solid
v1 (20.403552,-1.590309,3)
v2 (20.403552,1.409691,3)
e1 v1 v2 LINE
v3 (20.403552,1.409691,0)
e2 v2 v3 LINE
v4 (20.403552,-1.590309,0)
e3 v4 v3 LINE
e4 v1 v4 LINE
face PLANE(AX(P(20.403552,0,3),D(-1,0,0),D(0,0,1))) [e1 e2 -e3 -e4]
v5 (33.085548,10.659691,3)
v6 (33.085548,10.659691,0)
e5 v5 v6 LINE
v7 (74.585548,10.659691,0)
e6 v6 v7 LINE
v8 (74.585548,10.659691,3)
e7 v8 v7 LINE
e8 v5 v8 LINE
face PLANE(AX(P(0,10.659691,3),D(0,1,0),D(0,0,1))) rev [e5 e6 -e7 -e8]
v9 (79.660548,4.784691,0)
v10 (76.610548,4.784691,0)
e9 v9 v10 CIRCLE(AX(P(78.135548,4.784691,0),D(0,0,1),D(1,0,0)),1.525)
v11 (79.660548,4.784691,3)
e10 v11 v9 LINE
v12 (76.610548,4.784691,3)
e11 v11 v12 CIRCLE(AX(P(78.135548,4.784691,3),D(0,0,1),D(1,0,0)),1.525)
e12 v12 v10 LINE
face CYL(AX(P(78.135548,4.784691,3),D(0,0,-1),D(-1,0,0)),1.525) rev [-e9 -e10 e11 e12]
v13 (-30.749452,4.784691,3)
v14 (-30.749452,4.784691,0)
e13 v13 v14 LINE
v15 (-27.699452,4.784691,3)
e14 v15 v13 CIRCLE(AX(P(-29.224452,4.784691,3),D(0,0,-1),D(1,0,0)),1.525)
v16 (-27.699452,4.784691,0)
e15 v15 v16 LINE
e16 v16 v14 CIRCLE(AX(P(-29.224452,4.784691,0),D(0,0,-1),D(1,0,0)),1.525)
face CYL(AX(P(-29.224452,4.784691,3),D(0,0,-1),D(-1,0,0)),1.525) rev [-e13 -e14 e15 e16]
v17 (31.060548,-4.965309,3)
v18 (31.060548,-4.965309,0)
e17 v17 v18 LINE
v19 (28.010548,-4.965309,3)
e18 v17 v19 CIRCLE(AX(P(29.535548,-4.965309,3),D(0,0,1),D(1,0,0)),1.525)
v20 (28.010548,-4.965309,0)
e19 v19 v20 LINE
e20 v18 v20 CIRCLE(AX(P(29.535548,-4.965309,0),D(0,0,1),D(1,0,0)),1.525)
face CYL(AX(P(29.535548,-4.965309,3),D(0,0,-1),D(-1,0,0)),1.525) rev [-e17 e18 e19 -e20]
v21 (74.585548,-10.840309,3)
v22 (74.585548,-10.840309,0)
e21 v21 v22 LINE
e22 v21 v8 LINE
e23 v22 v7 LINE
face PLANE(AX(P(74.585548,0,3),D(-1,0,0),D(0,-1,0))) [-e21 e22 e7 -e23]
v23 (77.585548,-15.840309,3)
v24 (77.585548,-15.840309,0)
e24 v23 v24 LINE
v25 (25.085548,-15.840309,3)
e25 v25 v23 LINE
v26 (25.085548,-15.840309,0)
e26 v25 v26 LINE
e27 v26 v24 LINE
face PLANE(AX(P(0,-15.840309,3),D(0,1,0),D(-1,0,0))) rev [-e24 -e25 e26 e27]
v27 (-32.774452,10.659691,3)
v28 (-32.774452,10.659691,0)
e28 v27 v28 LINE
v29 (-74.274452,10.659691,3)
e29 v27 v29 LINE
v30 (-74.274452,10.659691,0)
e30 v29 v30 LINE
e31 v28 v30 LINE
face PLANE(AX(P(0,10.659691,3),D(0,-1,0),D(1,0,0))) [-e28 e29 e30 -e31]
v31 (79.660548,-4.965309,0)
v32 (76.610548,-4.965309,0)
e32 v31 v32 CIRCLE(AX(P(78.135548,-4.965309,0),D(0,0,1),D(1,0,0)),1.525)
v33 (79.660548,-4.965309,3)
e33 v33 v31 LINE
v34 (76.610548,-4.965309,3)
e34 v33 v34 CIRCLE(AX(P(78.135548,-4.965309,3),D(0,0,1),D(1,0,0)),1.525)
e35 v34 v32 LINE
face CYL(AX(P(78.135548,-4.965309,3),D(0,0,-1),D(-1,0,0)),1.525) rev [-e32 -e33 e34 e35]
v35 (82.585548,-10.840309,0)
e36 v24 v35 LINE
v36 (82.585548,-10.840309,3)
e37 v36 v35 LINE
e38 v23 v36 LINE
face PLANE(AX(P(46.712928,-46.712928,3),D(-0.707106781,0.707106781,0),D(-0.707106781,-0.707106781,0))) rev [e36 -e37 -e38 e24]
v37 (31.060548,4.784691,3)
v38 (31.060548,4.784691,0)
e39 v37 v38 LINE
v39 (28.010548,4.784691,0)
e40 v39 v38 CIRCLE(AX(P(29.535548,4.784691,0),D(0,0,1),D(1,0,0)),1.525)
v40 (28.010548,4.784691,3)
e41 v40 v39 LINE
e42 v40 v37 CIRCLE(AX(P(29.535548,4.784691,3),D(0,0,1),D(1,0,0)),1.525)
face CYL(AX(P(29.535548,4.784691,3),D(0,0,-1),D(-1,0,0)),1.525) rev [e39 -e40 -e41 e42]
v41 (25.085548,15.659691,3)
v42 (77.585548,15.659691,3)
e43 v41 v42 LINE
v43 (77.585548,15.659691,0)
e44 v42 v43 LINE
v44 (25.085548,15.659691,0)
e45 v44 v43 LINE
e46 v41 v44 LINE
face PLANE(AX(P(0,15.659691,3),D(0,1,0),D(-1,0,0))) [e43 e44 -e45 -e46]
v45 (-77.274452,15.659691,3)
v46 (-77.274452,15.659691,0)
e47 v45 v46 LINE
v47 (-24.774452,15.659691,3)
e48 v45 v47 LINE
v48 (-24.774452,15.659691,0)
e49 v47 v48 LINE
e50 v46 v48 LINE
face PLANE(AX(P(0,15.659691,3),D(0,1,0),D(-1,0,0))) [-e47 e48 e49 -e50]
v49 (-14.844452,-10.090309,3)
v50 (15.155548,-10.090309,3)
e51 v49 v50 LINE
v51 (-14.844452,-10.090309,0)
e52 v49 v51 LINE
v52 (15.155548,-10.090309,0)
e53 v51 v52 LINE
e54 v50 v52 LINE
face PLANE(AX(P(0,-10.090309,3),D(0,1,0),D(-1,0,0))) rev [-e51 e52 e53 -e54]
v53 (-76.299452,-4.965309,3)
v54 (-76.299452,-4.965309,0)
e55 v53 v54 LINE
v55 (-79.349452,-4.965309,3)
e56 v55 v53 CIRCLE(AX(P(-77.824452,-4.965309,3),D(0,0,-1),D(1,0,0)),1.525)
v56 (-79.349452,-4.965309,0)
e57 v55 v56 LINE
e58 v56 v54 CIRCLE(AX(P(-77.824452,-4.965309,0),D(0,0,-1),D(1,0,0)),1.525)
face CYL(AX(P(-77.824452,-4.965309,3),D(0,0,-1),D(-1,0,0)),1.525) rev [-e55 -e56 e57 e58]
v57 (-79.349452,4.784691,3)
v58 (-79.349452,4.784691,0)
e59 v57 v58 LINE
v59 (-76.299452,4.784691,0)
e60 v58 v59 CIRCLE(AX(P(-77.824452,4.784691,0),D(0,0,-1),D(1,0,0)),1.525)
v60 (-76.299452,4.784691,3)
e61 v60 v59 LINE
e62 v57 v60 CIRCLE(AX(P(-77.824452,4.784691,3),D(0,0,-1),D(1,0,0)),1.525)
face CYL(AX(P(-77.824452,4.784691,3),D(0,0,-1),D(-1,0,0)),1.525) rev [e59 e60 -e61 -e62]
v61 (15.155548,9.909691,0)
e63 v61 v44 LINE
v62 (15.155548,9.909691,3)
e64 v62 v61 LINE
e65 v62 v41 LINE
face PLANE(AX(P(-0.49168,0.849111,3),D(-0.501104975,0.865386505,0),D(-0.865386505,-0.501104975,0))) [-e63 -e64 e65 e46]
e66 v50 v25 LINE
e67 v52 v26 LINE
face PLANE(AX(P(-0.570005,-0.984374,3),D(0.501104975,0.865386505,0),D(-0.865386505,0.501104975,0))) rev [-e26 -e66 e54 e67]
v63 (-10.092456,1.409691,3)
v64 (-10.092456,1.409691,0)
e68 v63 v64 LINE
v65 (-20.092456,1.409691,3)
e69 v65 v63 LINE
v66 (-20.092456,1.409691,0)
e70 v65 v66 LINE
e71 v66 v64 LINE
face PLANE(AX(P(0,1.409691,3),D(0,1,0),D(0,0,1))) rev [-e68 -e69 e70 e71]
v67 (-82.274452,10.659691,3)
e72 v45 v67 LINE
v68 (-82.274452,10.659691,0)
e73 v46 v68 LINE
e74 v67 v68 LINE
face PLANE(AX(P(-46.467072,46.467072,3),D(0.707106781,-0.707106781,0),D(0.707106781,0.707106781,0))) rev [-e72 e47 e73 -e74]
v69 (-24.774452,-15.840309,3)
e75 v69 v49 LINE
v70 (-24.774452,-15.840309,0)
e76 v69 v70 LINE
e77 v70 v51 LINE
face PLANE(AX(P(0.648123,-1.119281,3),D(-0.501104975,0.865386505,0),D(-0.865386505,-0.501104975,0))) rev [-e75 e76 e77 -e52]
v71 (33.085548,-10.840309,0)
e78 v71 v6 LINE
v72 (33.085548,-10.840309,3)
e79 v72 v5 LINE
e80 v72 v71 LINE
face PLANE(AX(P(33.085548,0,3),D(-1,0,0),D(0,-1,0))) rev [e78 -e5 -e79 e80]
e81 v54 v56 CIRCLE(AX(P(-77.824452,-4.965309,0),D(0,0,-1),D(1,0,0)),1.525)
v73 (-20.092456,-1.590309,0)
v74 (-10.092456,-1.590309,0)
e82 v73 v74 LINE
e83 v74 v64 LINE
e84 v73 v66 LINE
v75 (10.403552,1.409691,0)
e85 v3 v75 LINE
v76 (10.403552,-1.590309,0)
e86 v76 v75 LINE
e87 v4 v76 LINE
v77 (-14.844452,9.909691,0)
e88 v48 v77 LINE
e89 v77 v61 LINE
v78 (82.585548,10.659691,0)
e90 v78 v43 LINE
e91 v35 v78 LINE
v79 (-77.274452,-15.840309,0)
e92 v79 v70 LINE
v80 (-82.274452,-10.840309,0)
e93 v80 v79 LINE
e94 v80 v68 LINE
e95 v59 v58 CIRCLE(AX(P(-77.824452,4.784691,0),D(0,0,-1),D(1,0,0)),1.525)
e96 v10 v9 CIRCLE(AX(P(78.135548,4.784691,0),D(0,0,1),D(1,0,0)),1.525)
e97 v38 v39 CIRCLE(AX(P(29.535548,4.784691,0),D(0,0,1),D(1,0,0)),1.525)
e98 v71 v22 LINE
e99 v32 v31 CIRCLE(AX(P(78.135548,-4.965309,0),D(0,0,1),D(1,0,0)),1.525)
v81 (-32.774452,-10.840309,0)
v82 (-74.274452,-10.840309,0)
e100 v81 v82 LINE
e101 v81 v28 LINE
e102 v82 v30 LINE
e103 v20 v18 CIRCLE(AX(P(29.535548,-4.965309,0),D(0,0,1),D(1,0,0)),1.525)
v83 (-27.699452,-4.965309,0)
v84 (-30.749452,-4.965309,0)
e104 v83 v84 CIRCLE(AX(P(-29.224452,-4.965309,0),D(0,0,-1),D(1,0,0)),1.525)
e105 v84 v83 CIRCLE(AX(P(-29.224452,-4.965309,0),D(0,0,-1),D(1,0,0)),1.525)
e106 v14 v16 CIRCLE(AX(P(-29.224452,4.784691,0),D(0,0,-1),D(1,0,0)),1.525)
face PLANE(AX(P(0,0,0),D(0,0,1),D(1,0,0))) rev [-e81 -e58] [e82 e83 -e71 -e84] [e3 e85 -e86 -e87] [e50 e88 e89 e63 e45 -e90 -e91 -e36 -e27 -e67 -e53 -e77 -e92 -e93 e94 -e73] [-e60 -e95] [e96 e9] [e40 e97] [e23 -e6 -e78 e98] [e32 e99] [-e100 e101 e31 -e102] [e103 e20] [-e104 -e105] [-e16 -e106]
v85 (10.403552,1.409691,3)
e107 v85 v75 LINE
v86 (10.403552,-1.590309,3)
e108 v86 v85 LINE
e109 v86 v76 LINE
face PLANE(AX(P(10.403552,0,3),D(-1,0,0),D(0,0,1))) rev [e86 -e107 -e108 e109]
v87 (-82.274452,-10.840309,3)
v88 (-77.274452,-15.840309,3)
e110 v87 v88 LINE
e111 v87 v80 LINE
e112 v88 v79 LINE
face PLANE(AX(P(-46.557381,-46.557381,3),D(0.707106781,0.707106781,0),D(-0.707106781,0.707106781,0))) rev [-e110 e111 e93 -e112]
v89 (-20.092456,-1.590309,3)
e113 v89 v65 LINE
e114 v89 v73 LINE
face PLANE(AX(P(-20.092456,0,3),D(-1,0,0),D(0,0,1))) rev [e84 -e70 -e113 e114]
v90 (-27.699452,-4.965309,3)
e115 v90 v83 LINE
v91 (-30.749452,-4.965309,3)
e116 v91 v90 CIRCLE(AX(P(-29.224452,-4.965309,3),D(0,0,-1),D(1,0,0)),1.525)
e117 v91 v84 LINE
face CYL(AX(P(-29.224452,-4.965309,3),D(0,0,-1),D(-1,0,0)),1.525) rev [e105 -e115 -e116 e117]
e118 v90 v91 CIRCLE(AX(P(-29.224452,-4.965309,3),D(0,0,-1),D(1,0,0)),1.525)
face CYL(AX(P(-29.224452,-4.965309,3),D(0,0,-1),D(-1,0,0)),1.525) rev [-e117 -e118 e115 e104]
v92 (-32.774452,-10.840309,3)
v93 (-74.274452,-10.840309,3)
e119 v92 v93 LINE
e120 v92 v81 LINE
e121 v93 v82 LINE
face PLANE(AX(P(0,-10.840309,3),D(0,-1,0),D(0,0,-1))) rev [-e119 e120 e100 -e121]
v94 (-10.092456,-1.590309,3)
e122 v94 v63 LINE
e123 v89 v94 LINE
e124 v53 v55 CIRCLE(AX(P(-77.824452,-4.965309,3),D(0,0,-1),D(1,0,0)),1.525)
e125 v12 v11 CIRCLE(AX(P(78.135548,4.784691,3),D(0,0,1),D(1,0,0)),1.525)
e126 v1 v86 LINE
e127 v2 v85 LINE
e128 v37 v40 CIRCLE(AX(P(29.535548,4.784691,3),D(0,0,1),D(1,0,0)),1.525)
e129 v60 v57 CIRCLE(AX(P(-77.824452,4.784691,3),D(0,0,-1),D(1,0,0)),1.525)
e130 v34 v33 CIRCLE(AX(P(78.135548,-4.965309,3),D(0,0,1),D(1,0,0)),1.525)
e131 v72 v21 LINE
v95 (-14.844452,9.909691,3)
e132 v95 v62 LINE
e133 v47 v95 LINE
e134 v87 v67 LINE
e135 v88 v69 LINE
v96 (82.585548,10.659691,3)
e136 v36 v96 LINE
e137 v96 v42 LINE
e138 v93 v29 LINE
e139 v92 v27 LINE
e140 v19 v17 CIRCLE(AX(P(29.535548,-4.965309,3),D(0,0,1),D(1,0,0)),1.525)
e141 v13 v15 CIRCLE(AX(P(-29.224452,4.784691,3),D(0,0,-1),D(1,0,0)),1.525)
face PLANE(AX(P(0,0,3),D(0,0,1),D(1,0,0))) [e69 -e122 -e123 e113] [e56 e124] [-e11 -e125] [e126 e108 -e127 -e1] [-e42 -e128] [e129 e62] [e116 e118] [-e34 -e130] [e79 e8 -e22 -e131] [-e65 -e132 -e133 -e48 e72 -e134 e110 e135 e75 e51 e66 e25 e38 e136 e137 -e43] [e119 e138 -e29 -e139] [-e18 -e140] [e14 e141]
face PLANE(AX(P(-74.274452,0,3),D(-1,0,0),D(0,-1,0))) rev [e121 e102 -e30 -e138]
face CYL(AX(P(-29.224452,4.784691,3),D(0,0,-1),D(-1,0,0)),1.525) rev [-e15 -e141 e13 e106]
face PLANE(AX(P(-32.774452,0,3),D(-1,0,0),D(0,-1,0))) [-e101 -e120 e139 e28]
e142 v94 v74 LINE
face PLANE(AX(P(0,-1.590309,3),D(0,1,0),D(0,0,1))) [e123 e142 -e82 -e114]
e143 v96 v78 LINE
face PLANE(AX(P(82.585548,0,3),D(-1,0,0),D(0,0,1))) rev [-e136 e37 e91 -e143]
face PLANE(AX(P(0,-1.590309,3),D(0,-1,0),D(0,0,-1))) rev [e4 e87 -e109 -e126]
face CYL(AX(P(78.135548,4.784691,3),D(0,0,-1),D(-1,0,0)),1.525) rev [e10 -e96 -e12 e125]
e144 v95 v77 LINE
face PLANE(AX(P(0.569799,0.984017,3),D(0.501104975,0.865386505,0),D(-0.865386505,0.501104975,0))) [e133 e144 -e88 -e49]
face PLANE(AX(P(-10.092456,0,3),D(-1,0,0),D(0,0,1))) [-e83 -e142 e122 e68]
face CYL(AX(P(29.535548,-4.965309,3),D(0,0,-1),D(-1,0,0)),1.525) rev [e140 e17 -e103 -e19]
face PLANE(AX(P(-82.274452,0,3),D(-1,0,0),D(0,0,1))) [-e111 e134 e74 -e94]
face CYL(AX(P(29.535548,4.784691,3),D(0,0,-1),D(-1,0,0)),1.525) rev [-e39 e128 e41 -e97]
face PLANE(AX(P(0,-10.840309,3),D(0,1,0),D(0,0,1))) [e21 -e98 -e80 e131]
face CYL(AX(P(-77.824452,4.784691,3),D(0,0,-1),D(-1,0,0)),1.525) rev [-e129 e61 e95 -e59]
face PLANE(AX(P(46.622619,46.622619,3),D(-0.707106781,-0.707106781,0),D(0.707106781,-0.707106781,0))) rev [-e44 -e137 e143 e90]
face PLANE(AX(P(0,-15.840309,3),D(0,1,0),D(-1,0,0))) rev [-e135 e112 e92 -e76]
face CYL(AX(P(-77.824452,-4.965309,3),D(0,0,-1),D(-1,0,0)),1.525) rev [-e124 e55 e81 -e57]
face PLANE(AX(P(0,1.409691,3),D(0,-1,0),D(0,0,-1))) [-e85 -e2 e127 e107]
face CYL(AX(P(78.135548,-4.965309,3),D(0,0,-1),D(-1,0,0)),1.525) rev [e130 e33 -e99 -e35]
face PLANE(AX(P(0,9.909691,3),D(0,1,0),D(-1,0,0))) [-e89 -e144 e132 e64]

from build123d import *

# Parameters (mm, degrees)
SKETCH_1_R      = 1.525
SKETCH_1_W      = 41.5
SKETCH_1_H      = 21.5
SKETCH_1_W_2    = 10
SKETCH_1_H_2    = 3
EXTRUDE_3_DEPTH = 3


with BuildPart() as part:
    # 草图1 → 凸台-拉伸3 (new body)
    with BuildSketch(Plane.XY):
        Polygon((-77.274452038, 15.659691017), (-82.274452038, 10.659691017), (-82.274452038, -10.840308983), (-77.274452038, -15.840308983), (-24.774452038, -15.840308983), (-14.844452038, -10.090308983), (15.155547962, -10.090308983), (25.085547962, -15.840308983), (77.585547962, -15.840308983), (82.585547962, -10.840308983), (82.585547962, 10.659691017), (77.585547962, 15.659691017), (25.085547962, 15.659691017), (15.155547962, 9.909691017), (-14.844452038, 9.909691017), (-24.774452038, 15.659691017), align=None)
        with Locations((78.135547962, 4.784691017)):
            Circle(SKETCH_1_R, mode=Mode.SUBTRACT)
        with Locations((78.135547962, -4.965308983)):
            Circle(SKETCH_1_R, mode=Mode.SUBTRACT)
        with Locations((-77.824452038, -4.965308983)):
            Circle(SKETCH_1_R, mode=Mode.SUBTRACT)
        with Locations((-77.824452038, 4.784691017)):
            Circle(SKETCH_1_R, mode=Mode.SUBTRACT)
        with Locations((29.535547962, 4.784691017)):
            Circle(SKETCH_1_R, mode=Mode.SUBTRACT)
        with Locations((29.535547962, -4.965308983)):
            Circle(SKETCH_1_R, mode=Mode.SUBTRACT)
        with Locations((-29.224452038, -4.965308983)):
            Circle(SKETCH_1_R, mode=Mode.SUBTRACT)
        with Locations((-29.224452038, 4.784691017)):
            Circle(SKETCH_1_R, mode=Mode.SUBTRACT)
        with Locations((-53.524452038, -0.090308983)):
            Rectangle(SKETCH_1_W, SKETCH_1_H, mode=Mode.SUBTRACT)
        with Locations((53.835547962, -0.090308983)):
            Rectangle(SKETCH_1_W, SKETCH_1_H, mode=Mode.SUBTRACT)
        with Locations((15.403552423, -0.090308983)):
            Rectangle(SKETCH_1_W_2, SKETCH_1_H_2, mode=Mode.SUBTRACT)
        with Locations((-15.092456498, -0.090308983)):
            Rectangle(SKETCH_1_W_2, SKETCH_1_H_2, mode=Mode.SUBTRACT)
    extrude(amount=EXTRUDE_3_DEPTH)


solid = part.part
